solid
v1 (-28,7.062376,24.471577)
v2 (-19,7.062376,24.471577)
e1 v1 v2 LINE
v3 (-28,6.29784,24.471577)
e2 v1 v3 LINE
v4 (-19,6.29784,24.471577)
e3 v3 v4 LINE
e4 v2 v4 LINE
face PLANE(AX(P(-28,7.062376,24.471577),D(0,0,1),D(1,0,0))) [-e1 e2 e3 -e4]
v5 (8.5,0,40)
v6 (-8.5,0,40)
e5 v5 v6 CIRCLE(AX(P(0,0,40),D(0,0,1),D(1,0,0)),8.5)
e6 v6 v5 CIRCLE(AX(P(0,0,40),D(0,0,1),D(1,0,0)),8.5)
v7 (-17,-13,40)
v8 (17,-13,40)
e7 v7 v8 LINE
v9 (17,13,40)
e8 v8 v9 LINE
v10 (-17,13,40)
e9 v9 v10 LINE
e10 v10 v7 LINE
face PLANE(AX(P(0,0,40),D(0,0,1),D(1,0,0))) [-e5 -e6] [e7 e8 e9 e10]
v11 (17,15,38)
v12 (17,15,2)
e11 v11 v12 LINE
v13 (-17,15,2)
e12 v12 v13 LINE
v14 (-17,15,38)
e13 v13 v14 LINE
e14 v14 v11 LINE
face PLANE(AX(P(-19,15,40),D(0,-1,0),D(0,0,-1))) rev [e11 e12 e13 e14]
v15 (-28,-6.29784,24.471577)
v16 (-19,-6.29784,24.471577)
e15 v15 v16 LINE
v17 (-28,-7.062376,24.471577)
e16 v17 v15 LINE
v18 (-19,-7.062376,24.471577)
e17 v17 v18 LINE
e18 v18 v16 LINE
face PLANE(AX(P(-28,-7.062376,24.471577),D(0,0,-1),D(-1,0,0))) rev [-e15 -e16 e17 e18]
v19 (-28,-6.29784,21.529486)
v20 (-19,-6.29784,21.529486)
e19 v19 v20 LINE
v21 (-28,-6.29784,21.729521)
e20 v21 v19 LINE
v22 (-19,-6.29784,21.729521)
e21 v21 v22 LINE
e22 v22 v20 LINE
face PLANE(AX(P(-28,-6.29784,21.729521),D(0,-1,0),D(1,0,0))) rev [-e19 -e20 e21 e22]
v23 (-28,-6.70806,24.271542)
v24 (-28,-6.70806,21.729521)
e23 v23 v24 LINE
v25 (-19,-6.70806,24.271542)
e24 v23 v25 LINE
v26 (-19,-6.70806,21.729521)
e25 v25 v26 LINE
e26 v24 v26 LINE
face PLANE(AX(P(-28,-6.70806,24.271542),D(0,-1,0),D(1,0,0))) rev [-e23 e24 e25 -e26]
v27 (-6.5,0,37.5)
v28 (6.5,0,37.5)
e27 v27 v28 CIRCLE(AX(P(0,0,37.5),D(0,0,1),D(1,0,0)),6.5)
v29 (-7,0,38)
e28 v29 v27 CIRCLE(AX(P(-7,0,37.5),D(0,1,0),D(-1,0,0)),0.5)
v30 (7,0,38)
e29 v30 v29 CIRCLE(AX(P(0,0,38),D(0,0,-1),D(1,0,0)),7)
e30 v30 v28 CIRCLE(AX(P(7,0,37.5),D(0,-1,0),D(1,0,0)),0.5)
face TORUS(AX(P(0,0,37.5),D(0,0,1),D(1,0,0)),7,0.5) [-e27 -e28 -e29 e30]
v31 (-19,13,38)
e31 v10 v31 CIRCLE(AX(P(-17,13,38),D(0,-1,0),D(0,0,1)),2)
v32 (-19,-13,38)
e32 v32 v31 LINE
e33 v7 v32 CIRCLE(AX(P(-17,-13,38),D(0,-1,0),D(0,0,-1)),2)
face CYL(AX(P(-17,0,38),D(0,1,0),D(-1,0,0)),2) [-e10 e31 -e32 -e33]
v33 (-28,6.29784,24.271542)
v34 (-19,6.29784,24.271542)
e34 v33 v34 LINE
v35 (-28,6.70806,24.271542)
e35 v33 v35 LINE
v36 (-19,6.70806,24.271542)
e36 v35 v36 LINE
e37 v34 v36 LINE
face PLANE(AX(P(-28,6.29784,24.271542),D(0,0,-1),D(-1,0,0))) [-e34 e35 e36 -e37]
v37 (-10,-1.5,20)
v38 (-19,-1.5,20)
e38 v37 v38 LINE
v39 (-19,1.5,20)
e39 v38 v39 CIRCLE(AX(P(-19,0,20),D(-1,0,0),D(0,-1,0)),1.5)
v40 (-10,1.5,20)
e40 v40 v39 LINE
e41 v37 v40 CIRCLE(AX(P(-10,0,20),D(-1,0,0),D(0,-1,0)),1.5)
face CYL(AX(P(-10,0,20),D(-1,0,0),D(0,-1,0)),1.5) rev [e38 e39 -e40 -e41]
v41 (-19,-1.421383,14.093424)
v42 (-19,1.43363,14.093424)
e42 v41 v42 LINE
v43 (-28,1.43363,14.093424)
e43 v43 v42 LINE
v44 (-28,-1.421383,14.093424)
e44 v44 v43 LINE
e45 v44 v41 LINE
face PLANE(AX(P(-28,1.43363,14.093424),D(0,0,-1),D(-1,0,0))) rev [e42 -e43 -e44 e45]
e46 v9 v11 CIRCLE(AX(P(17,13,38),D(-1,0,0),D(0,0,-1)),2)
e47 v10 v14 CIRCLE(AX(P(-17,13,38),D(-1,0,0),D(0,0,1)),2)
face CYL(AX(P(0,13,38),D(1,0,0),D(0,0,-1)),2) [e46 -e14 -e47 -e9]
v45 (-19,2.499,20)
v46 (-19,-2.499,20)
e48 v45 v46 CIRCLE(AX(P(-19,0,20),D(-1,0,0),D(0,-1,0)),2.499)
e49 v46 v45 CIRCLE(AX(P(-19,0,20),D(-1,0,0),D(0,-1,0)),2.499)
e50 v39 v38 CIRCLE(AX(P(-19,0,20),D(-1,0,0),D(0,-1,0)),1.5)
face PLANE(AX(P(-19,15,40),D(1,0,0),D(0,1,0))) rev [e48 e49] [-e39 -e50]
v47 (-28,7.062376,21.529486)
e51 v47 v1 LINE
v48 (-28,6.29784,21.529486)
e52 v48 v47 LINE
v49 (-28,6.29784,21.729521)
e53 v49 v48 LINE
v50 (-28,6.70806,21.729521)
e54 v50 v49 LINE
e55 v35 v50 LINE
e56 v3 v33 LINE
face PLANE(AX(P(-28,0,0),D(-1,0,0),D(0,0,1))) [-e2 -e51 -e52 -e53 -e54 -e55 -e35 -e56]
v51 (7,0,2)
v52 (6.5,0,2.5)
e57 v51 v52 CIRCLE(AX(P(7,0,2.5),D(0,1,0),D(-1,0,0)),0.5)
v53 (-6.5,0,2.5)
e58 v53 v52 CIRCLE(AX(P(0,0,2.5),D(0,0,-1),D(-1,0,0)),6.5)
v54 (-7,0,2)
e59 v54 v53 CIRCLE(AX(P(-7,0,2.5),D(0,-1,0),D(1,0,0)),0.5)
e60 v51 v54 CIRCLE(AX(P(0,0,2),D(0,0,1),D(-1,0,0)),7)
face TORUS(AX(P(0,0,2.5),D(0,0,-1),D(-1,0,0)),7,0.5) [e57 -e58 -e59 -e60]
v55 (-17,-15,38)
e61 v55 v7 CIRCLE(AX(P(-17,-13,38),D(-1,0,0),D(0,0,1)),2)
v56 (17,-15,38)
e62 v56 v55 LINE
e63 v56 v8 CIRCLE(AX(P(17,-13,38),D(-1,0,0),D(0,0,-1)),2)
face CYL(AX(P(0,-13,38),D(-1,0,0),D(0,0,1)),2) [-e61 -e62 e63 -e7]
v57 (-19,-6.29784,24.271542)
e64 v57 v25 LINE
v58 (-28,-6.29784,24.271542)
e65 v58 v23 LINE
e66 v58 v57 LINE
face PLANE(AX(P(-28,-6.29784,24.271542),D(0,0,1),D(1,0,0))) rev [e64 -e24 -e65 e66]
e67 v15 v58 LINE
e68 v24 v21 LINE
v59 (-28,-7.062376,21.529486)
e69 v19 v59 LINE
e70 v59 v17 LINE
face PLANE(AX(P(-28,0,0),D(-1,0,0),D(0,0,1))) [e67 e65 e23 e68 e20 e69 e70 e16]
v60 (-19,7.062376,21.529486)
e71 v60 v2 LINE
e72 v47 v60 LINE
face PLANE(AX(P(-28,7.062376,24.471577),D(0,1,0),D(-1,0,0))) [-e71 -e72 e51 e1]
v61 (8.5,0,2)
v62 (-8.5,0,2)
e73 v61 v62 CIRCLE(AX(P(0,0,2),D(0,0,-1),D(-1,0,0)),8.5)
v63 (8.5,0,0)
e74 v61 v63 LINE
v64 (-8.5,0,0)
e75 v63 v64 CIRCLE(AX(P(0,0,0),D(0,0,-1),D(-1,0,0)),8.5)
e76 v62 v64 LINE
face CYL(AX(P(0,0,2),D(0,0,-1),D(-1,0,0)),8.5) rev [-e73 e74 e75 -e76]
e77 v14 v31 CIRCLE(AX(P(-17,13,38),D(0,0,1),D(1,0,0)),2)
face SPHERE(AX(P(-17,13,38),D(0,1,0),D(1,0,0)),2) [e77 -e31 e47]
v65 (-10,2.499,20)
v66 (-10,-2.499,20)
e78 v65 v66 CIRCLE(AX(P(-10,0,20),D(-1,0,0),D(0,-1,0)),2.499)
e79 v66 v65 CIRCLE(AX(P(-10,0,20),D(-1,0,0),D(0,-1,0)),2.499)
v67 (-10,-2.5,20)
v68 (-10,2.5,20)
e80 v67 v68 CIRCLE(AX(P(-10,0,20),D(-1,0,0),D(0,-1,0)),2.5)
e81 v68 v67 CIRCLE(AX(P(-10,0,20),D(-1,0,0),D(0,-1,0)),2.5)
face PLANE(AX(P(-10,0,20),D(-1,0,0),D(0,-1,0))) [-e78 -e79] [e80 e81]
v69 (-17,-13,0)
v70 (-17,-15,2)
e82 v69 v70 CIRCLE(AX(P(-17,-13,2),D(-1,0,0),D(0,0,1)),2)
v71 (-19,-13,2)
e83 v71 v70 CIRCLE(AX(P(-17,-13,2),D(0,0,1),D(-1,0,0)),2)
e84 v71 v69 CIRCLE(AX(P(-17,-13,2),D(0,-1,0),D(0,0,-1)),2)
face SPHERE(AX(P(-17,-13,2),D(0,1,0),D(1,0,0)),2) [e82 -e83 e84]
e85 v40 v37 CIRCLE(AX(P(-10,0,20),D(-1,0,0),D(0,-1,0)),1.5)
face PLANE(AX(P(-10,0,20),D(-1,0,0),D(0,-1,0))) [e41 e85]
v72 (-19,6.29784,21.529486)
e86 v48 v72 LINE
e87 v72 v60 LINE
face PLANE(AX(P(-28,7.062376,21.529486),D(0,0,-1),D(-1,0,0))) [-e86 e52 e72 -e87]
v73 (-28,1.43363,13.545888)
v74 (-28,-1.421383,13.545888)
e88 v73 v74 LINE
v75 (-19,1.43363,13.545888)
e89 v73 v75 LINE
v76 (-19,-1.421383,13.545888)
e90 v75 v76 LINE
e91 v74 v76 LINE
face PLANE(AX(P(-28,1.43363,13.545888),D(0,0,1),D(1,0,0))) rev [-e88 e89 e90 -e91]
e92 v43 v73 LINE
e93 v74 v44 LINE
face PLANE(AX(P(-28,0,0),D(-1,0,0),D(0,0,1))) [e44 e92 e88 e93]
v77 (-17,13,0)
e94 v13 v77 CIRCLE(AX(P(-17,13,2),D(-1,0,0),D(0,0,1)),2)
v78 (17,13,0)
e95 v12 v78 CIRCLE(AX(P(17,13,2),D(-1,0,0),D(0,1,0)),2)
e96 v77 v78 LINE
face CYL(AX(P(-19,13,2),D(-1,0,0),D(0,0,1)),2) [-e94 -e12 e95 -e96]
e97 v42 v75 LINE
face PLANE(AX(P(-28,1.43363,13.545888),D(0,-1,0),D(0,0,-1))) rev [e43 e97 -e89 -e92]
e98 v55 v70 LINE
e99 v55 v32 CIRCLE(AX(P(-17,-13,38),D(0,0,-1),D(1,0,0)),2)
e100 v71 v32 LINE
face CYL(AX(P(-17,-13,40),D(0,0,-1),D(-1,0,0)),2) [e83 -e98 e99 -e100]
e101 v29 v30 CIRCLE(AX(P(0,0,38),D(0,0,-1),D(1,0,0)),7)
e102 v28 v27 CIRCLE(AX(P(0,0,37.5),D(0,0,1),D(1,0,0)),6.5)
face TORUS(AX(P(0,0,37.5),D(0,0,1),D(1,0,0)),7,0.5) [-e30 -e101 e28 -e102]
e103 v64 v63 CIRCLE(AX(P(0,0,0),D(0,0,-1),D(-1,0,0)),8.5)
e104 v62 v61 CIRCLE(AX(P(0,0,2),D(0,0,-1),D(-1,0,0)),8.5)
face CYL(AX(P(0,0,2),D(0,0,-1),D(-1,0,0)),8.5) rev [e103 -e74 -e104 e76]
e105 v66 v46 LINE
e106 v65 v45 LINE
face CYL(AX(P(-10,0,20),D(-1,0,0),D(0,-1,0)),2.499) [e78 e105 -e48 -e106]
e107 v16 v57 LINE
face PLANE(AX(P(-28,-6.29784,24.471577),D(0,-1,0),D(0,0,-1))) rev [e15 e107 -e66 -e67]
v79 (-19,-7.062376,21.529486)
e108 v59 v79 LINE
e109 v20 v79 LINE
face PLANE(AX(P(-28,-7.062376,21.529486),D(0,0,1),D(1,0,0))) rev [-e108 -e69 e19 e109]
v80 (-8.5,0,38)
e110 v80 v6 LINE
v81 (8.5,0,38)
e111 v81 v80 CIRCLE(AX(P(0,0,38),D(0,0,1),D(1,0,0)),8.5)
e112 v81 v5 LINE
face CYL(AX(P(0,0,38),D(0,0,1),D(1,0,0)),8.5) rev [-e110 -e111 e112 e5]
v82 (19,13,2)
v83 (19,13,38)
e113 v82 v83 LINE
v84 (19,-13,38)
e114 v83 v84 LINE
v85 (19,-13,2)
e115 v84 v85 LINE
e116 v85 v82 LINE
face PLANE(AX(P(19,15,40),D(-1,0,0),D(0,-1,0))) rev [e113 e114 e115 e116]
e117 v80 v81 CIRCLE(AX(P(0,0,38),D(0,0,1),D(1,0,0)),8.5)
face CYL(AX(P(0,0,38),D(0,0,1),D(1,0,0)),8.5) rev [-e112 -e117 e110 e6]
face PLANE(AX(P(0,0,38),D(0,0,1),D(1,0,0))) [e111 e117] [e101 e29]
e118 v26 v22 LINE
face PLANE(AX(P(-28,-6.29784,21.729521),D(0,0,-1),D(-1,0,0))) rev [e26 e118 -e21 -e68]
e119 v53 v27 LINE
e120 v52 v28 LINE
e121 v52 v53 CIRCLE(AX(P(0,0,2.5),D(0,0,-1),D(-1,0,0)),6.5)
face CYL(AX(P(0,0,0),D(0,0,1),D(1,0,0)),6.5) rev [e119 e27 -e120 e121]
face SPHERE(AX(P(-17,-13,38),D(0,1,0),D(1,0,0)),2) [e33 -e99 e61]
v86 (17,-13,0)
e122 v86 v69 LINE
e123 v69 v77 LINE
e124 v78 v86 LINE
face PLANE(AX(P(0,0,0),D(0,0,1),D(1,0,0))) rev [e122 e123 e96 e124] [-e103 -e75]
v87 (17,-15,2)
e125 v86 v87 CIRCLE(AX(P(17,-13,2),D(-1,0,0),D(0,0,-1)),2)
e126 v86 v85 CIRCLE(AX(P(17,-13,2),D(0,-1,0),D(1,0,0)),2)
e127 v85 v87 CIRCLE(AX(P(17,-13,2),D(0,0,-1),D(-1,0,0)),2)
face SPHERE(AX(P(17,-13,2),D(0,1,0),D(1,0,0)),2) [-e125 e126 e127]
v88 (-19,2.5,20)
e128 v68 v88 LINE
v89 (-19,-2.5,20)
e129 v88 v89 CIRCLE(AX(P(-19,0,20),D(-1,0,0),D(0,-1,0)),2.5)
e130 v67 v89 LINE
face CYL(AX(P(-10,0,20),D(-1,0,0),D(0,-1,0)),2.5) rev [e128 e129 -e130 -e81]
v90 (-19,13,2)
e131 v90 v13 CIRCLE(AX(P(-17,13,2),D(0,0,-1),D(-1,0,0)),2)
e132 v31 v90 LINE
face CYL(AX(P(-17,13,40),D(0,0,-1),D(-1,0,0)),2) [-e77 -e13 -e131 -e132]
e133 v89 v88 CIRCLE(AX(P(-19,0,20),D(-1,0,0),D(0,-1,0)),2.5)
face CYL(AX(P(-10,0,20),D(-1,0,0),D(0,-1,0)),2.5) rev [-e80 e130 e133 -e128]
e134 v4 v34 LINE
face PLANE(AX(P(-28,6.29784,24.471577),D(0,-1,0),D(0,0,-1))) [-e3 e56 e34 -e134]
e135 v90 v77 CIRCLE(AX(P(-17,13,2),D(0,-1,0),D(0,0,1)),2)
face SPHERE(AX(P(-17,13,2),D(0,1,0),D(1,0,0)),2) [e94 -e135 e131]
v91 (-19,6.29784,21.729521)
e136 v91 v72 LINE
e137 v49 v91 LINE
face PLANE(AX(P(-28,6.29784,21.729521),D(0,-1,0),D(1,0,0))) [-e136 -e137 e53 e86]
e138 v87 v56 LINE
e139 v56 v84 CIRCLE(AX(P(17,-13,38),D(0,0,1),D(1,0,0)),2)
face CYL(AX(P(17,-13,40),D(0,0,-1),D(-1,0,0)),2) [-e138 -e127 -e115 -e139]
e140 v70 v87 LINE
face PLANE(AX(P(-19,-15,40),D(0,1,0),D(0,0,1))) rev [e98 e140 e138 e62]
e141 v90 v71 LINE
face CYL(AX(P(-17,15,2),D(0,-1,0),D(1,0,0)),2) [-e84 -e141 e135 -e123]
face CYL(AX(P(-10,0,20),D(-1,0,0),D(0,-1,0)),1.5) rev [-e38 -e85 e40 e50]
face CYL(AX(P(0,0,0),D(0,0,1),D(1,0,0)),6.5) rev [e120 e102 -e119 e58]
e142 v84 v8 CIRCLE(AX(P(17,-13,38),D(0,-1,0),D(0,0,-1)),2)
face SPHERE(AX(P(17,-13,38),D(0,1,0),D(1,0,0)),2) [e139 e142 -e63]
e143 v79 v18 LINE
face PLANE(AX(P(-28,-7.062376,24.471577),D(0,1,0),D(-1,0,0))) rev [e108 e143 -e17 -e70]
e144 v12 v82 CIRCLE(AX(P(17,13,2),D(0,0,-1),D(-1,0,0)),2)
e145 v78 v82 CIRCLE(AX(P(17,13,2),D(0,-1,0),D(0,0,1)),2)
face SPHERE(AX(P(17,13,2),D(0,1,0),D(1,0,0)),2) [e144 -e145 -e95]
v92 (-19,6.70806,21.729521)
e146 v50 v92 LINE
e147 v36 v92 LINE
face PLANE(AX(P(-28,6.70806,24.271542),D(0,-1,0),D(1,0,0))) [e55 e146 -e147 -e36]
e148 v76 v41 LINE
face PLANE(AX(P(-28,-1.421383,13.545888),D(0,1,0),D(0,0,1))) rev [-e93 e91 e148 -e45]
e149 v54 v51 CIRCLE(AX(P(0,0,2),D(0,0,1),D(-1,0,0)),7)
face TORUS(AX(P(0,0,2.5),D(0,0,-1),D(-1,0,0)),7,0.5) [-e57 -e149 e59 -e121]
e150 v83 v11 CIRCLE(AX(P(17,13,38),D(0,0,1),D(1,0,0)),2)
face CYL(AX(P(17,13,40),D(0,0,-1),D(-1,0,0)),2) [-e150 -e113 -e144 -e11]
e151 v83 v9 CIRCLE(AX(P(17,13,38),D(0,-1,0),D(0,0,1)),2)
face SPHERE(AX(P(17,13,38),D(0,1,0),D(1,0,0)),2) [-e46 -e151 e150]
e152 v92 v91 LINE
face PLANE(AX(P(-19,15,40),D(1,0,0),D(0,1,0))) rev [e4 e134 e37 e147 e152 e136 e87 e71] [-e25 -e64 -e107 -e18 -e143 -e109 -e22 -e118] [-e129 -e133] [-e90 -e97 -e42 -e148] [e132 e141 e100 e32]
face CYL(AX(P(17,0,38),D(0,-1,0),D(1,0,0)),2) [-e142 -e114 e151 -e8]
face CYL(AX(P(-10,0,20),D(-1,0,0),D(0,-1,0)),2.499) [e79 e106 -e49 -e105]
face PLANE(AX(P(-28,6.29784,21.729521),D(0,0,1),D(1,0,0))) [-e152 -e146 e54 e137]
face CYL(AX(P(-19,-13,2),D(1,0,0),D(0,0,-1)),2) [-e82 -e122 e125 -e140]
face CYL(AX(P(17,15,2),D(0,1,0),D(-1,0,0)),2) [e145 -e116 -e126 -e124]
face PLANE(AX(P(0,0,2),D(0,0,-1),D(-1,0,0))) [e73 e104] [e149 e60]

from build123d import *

# Parameters (mm, degrees)
SKETCH1_W           = 38
SKETCH1_H           = 30
BOSS_EXTRUDE1_DEPTH = 40
FILLET1_R           = 2
SKETCH2_R           = 6.5
CUT_EXTRUDE1_DEPTH  = 40
SKETCH3_R           = 8.5
CUT_EXTRUDE2_DEPTH  = 2
CUT_EXTRUDE3_START  = -2
SKETCH4_R           = 8.5
CUT_EXTRUDE3_DEPTH  = 2
FILLET2_R           = 0.5
SKETCH5_R           = 1.5
CUT_EXTRUDE4_DEPTH  = 9
SKETCH6_R           = 2.5
SKETCH6_R_2         = 2.499
CUT_EXTRUDE5_DEPTH  = 9
BOSS_EXTRUDE2_DEPTH = 9
SKETCH8_W           = 0.547536787
SKETCH8_H           = 2.855013248
BOSS_EXTRUDE3_DEPTH = 9


with BuildPart() as part:
    # Sketch1 → Boss-Extrude1 (new body)
    with BuildSketch(Plane.XY):
        Rectangle(SKETCH1_W, SKETCH1_H)
    extrude(amount=BOSS_EXTRUDE1_DEPTH)

    # Fillet1
    fillet1_edges = [part.edges().sort_by_distance(p)[0] for p in [
        (-19, 0, 40),
        (0, -15, 40),
        (19, 0, 40),
        (0, -15, 0),
        (-19, 0, 0),
        (0, 15, 0),
        (19, 0, 0),
        (19, -15, 20),
        (-19, -15, 20),
        (-19, 15, 20),
        (19, 15, 20),
        (0, 15, 40),
    ]]
    fillet(fillet1_edges, radius=FILLET1_R)

    # Sketch2 → Cut-Extrude1 (cut)
    with BuildSketch(Plane.XY.offset(40)):
        Circle(SKETCH2_R)
    extrude(amount=-CUT_EXTRUDE1_DEPTH, mode=Mode.SUBTRACT)

    # Sketch3 → Cut-Extrude2 (cut)
    with BuildSketch(Plane.XY.offset(40)):
        Circle(SKETCH3_R)
    extrude(amount=-CUT_EXTRUDE2_DEPTH, mode=Mode.SUBTRACT)

    # Sketch4 → Cut-Extrude3 (cut)
    with BuildSketch(Plane(origin=(0, 0, 0), x_dir=(-1, 0, 0), z_dir=(0, 0, -1)).offset(CUT_EXTRUDE3_START)):
        with Locations(Location((0, 0, 0), (0, 0, 180))):
            Circle(SKETCH4_R)
    extrude(amount=CUT_EXTRUDE3_DEPTH, mode=Mode.SUBTRACT)

    # Fillet2
    fillet2_edges = [part.edges().sort_by_distance(p)[0] for p in [
        (-6.5, 0, 38),
        (-6.5, 0, 2),
    ]]
    fillet(fillet2_edges, radius=FILLET2_R)

    # Sketch5 → Cut-Extrude4 (cut)
    with BuildSketch(Plane.ZY.offset(19)):
        with Locations(Location((20, 0, 0), (0, 0, 270))):
            Circle(SKETCH5_R)
    extrude(amount=-CUT_EXTRUDE4_DEPTH, mode=Mode.SUBTRACT)

    # Sketch6 → Cut-Extrude5 (cut)
    with BuildSketch(Plane.ZY.offset(19)):
        with Locations(Location((20, 0, 0), (0, 0, 270))):
            Circle(SKETCH6_R)
        with Locations(Location((20, 0, 0), (0, 0, 270))):
            Circle(SKETCH6_R_2, mode=Mode.SUBTRACT)
    extrude(amount=-CUT_EXTRUDE5_DEPTH, mode=Mode.SUBTRACT)

    # Sketch7 → Boss-Extrude2 (add)
    with BuildSketch(Plane.ZY.offset(19)):
        Polygon((21.729521331, -6.29783972), (21.529486226, -6.29783972), (21.529486226, -7.062375907), (24.471577179, -7.062375907), (24.471577179, -6.29783972), (24.271542075, -6.29783972), (24.271542075, -6.708059845), (21.729521331, -6.708059845), align=None)
    boss_extrude2 = extrude(amount=BOSS_EXTRUDE2_DEPTH)

    # Mirror1: Boss-Extrude2 across plane
    add(boss_extrude2.mirror(Plane.ZX))

    # Sketch8 → Boss-Extrude3 (add)
    with BuildSketch(Plane.ZY.offset(19)):
        with Locations((13.819655902, 0.006123147)):
            Rectangle(SKETCH8_W, SKETCH8_H)
    extrude(amount=BOSS_EXTRUDE3_DEPTH)


solid = part.part
